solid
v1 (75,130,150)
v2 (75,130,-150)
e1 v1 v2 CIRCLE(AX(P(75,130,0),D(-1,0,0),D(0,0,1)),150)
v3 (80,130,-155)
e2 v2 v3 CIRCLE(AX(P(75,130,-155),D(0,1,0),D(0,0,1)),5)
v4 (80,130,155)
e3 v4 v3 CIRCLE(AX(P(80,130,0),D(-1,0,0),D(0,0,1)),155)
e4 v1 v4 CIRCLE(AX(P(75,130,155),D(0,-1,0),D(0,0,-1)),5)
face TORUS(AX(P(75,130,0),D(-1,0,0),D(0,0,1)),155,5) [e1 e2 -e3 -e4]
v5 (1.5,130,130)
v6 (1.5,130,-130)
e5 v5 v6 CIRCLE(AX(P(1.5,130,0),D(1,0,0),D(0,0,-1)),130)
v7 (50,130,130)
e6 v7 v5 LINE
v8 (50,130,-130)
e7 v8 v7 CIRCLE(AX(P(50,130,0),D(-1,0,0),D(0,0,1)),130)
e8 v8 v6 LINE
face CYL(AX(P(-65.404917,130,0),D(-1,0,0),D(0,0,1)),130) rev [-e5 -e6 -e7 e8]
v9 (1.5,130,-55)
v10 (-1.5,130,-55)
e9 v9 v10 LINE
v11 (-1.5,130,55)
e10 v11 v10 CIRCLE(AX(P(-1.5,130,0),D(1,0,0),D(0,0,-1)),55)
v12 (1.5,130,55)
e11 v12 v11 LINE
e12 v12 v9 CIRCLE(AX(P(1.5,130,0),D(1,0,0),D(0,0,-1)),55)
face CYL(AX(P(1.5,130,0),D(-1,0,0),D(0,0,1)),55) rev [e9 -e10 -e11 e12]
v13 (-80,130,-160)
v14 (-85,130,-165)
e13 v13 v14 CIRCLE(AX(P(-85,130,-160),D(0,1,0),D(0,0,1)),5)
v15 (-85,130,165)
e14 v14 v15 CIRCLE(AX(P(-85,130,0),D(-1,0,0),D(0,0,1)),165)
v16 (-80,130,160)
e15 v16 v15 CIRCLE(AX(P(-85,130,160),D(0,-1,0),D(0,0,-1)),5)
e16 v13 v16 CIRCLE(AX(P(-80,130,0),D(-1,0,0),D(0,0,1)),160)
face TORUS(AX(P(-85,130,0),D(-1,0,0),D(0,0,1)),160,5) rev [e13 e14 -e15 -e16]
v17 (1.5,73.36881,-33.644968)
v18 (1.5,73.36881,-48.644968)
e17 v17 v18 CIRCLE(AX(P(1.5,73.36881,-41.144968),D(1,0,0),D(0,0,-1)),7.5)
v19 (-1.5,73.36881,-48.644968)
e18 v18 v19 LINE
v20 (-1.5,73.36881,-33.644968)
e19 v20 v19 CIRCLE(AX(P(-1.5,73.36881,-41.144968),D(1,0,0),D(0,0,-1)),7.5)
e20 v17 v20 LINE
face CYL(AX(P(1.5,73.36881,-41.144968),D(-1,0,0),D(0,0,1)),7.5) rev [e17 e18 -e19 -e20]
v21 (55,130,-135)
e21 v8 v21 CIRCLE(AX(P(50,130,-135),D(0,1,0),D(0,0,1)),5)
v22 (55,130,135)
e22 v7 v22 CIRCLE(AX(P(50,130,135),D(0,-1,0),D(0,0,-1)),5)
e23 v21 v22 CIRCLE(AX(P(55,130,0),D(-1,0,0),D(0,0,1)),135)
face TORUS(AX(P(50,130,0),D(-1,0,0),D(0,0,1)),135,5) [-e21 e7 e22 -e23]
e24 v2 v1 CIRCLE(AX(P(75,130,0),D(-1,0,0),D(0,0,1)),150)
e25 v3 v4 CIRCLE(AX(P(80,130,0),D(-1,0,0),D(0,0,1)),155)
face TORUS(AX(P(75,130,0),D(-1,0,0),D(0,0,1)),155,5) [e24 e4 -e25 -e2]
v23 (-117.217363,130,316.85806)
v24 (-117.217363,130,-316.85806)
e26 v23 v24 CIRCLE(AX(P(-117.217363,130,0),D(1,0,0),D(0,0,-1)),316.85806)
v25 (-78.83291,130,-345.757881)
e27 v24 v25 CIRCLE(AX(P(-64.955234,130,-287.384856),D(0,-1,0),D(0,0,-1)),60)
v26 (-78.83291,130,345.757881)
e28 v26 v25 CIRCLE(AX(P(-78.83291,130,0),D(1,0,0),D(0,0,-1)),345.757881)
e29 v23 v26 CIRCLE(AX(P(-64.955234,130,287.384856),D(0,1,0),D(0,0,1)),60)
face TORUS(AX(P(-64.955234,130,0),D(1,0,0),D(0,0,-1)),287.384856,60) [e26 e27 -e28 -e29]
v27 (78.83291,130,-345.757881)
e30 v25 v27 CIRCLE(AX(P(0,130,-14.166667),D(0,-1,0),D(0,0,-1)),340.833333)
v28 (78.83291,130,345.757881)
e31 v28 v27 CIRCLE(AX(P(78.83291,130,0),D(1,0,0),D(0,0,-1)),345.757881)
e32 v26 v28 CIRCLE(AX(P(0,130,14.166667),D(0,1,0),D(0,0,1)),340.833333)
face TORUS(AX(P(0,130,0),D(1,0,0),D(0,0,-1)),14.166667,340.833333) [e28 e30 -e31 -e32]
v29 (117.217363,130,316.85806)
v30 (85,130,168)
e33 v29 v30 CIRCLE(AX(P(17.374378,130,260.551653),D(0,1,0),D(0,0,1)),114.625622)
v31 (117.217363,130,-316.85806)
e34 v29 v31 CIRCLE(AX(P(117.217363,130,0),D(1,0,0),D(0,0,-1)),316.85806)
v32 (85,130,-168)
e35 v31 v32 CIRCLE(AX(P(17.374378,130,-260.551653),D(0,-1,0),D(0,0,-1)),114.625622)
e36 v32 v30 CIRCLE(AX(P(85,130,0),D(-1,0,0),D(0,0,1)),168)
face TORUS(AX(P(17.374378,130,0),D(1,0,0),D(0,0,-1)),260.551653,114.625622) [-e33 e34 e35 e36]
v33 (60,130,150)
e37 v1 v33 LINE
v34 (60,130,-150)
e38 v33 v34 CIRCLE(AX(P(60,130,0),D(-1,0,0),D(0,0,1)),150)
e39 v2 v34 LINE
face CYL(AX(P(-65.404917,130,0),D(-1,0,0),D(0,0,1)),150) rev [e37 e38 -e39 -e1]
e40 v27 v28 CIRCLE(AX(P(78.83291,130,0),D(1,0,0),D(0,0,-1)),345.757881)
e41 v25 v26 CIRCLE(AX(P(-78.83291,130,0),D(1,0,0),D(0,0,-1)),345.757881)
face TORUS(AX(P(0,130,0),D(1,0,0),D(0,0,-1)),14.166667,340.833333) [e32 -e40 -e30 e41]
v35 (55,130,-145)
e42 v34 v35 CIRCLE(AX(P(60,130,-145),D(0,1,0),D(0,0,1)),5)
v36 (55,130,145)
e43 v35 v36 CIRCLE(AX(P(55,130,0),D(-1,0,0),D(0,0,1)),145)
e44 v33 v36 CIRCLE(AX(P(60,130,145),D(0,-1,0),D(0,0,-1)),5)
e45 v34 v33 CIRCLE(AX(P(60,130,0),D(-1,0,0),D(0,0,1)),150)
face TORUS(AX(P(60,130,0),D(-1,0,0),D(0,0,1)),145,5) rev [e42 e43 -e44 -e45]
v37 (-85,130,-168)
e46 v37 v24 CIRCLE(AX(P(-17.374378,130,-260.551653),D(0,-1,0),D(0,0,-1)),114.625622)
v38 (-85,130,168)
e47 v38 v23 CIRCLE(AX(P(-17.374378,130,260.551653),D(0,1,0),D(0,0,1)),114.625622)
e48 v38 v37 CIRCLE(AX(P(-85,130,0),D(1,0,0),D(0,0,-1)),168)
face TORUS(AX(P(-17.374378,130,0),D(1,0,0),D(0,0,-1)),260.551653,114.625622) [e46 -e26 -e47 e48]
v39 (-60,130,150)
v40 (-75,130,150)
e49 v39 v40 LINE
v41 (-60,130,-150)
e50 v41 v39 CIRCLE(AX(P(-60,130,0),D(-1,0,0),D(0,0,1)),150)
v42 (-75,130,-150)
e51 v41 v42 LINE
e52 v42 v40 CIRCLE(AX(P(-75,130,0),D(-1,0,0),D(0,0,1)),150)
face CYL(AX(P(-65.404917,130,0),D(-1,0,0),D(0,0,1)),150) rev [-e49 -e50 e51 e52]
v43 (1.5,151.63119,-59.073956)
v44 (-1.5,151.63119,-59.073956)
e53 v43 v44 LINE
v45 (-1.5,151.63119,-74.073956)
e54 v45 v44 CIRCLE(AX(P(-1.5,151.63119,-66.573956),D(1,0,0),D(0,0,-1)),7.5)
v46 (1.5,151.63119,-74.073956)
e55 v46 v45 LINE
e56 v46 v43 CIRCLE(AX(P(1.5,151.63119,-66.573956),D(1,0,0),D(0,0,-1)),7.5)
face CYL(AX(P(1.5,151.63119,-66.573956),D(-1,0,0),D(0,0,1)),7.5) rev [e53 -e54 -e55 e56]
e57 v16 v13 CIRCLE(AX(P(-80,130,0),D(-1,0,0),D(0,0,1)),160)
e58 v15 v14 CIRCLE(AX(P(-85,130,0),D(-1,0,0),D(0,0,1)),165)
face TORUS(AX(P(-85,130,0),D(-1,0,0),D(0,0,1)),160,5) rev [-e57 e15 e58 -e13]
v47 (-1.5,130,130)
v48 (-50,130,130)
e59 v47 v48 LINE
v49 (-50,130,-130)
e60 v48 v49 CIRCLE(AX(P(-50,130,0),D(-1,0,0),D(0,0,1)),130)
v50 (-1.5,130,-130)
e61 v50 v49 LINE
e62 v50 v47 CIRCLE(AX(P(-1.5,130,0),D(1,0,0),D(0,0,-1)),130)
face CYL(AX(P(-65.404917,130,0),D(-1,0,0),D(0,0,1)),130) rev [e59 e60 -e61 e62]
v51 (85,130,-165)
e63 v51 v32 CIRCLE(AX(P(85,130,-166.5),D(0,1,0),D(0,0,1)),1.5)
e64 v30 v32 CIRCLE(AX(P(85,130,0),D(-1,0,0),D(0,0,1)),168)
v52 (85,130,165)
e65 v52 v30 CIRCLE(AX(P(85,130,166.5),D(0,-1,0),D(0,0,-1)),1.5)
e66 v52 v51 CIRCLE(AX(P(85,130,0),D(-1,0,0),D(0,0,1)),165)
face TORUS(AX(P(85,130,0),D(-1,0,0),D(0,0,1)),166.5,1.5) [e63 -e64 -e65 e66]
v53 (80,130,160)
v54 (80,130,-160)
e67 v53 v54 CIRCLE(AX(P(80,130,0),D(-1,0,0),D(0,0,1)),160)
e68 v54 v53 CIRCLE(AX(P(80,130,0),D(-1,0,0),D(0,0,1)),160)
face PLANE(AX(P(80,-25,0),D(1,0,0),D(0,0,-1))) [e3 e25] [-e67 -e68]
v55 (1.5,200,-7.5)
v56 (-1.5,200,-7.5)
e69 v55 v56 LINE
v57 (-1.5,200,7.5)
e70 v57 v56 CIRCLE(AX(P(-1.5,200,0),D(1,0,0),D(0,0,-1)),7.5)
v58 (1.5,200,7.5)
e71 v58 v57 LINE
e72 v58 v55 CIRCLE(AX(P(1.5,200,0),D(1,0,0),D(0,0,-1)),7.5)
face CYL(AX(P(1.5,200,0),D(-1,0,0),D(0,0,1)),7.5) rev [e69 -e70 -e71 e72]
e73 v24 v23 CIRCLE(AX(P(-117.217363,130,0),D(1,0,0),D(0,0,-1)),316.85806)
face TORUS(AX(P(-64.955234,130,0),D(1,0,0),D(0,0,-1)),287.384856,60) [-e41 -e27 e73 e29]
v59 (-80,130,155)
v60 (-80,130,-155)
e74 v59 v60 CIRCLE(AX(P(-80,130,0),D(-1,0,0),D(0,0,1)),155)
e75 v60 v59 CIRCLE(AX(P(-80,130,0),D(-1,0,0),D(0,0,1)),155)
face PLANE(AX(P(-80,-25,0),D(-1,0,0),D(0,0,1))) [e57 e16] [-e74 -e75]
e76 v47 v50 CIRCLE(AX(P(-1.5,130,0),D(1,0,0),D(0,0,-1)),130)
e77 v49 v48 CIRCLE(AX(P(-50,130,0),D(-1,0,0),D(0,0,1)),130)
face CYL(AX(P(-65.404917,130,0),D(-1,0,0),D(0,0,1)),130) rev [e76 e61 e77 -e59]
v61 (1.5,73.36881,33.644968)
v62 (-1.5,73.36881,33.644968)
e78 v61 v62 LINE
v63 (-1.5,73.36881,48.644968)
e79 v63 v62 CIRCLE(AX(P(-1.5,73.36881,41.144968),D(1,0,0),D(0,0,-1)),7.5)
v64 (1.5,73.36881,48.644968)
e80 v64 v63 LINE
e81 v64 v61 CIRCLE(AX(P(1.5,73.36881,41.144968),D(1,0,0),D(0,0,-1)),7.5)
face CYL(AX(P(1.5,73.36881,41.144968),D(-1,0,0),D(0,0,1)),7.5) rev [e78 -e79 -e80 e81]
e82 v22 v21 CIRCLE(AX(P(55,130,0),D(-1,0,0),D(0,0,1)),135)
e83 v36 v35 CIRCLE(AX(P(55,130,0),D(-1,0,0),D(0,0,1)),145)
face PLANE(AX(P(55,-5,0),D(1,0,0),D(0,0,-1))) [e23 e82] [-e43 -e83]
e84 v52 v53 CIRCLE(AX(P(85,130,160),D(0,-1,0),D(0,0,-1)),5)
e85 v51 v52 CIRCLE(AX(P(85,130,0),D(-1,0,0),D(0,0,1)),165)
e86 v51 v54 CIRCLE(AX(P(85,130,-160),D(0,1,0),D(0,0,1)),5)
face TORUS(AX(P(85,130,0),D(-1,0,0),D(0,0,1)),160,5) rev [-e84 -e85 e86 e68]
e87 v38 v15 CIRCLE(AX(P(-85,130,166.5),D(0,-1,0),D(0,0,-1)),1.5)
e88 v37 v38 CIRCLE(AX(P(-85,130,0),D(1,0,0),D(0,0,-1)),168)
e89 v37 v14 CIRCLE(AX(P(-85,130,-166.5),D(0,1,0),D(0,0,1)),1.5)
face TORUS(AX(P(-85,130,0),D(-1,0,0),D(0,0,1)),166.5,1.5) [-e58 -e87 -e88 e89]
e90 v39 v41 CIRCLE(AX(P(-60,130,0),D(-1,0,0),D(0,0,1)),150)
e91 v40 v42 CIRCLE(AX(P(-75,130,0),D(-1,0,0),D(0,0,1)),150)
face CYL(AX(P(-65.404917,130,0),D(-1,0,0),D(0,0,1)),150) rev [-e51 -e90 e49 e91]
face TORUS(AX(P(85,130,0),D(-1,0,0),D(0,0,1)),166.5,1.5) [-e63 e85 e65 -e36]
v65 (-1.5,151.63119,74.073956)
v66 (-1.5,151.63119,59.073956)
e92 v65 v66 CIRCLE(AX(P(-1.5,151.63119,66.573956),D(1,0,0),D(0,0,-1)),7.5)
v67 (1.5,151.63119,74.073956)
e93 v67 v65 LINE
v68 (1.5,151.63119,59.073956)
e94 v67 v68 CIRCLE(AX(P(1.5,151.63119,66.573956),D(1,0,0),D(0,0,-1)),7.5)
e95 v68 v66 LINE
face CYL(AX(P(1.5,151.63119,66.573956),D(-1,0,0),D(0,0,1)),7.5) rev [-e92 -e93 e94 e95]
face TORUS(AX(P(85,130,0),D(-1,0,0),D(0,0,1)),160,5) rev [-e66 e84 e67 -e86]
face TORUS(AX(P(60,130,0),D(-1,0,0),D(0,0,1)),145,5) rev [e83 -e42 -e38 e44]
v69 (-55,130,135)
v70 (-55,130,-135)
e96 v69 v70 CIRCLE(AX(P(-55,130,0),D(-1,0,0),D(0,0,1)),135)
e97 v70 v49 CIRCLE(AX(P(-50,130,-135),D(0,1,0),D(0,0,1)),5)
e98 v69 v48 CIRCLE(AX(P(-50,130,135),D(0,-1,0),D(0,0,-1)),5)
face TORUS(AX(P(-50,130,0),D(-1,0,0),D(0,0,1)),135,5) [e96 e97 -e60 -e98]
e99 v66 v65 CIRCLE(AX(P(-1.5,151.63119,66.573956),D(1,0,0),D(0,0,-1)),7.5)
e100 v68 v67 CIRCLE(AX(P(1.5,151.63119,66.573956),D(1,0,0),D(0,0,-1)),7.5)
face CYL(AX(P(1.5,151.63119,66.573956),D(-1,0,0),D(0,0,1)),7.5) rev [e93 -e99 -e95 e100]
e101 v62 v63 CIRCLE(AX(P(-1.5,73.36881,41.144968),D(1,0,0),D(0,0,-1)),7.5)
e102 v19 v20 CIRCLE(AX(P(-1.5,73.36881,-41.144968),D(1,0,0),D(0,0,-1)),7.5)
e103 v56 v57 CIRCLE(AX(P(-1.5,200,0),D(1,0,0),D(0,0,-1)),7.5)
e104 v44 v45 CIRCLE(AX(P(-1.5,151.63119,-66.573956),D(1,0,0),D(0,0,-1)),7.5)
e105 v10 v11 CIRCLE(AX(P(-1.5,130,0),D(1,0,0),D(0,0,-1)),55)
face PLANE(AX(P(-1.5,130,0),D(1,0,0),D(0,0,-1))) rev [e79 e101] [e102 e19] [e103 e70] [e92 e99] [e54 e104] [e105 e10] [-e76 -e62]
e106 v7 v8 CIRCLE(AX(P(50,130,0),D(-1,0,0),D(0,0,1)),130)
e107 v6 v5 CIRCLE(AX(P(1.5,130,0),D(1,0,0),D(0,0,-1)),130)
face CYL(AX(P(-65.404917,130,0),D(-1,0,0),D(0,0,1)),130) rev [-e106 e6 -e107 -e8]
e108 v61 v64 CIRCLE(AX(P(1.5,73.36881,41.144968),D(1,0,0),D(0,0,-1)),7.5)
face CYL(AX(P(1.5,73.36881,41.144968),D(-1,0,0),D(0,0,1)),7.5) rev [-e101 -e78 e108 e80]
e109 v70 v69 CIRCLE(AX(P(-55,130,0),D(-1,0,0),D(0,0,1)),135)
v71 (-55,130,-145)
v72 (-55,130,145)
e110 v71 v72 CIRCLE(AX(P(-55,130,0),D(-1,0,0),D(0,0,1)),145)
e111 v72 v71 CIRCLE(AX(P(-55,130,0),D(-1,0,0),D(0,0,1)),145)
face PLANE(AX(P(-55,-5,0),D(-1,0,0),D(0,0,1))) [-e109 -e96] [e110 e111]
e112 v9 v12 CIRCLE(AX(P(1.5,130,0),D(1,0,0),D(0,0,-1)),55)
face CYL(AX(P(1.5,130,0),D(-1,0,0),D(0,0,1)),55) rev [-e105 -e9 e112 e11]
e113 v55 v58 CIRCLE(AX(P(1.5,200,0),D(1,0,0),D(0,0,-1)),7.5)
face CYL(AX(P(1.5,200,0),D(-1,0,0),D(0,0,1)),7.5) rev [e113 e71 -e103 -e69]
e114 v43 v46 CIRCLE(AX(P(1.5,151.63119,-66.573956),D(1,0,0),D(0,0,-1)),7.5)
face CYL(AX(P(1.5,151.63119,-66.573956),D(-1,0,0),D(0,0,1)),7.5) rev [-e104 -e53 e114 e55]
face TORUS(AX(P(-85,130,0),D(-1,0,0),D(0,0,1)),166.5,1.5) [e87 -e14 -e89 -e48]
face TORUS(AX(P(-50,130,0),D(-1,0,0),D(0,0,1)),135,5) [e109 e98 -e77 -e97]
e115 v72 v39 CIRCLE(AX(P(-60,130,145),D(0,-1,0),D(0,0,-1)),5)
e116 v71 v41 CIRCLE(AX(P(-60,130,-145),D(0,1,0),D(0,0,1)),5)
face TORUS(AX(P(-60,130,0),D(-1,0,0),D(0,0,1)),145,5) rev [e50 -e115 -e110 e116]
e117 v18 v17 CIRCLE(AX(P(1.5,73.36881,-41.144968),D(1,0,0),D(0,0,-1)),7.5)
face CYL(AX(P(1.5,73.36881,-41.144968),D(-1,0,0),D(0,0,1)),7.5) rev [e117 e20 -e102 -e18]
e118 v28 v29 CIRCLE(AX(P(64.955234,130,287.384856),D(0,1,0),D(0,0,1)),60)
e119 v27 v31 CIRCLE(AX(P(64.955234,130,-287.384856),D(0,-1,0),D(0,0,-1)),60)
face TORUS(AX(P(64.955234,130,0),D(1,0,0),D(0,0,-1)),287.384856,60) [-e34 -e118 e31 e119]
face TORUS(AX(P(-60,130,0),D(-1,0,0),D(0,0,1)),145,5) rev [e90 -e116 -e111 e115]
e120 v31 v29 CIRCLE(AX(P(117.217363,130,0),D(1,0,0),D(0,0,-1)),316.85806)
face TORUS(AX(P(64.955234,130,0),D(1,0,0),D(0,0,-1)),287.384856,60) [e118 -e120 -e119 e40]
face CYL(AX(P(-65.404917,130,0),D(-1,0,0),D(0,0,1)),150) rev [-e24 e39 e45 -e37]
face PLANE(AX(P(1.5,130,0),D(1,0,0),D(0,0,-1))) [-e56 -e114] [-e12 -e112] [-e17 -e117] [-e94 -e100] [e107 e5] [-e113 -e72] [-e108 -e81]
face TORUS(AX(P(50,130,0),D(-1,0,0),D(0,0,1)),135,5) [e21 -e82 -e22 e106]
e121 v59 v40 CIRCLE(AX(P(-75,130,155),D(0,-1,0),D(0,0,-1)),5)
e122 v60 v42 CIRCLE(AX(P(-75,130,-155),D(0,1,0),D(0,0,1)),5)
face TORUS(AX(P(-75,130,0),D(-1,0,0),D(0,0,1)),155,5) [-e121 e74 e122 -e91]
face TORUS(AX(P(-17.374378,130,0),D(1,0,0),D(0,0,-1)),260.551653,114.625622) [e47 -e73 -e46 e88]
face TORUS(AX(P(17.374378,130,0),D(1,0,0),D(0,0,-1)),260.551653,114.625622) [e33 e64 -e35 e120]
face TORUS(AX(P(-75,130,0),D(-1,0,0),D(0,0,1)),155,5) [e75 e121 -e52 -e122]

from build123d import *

# Parameters (mm, degrees)
SKETCH_2_R      = 130
SKETCH_2_R_2    = 55
SKETCH_2_R_3    = 7.5
EXTRUDE_1_DEPTH = 1.5


with BuildPart() as part:
    # 草图1 → 旋转1 (revolve)
    with BuildSketch(Plane.XY, mode=Mode.PRIVATE) as revolve_1_sk:
        with BuildLine():
            Line((-50, 0), (50, 0))
            ThreePointArc((50, 0), (53.535533906, -1.464466094), (55, -5))
            Line((55, -5), (55, -15))
            ThreePointArc((55, -15), (56.464466094, -18.535533906), (60, -20))
            Line((60, -20), (75, -20))
            ThreePointArc((75, -20), (78.535533906, -21.464466094), (80, -25))
            Line((80, -25), (80, -30))
            ThreePointArc((80, -30), (81.464466094, -33.535533906), (85, -35))
            ThreePointArc((85, -35), (86.5, -36.5), (85, -38))
            ThreePointArc((85, -38), (79.343145751, -35.656854249), (77, -30))
            Line((77, -30), (77, -25))
            ThreePointArc((77, -25), (76.414213562, -23.585786438), (75, -23))
            Line((75, -23), (60, -23))
            ThreePointArc((60, -23), (54.343145751, -20.656854249), (52, -15))
            Line((52, -15), (52, -5))
            ThreePointArc((52, -5), (51.414213562, -3.585786438), (50, -3))
            Line((50, -3), (-50, -3))
            ThreePointArc((-50, -3), (-51.414213562, -3.585786438), (-52, -5))
            Line((-52, -5), (-52, -15))
            ThreePointArc((-52, -15), (-54.343145751, -20.656854249), (-60, -23))
            Line((-60, -23), (-75, -23))
            ThreePointArc((-75, -23), (-76.414213562, -23.585786438), (-77, -25))
            Line((-77, -25), (-77, -30))
            ThreePointArc((-77, -30), (-79.343145751, -35.656854249), (-85, -38))
            ThreePointArc((-85, -38), (-86.5, -36.5), (-85, -35))
            ThreePointArc((-85, -35), (-81.464466094, -33.535533906), (-80, -30))
            Line((-80, -30), (-80, -25))
            ThreePointArc((-80, -25), (-78.535533906, -21.464466094), (-75, -20))
            Line((-75, -20), (-60, -20))
            ThreePointArc((-60, -20), (-56.464466094, -18.535533906), (-55, -15))
            Line((-55, -15), (-55, -5))
            ThreePointArc((-55, -5), (-53.535533906, -1.464466094), (-50, 0))
        make_face()
    revolve(revolve_1_sk.sketch.rotate(Axis((-65.404917461, 130, 0), (1, 0, 0)), 270), axis=Axis((-65.404917461, 130, 0), (1, 0, 0)))



with BuildPart() as body_2:
    # 草图2 → 凸台-拉伸1 (new, symmetric)
    with BuildSketch(Plane(origin=(0, 0, 0), x_dir=(0, 0, -1), z_dir=(1, 0, 0))):
        with Locations(Location((0, 130, 0), (0, 0, 180))):
            Circle(SKETCH_2_R)
        with Locations((0, 130)):
            Circle(SKETCH_2_R_2, mode=Mode.SUBTRACT)
        with Locations((0, 200)):
            Circle(SKETCH_2_R_3, mode=Mode.SUBTRACT)
        with Locations((66.573956141, 151.631189606)):
            Circle(SKETCH_2_R_3, mode=Mode.SUBTRACT)
        with Locations((41.14496766, 73.368810394)):
            Circle(SKETCH_2_R_3, mode=Mode.SUBTRACT)
        with Locations((-41.14496766, 73.368810394)):
            Circle(SKETCH_2_R_3, mode=Mode.SUBTRACT)
        with Locations((-66.573956141, 151.631189606)):
            Circle(SKETCH_2_R_3, mode=Mode.SUBTRACT)
    extrude(amount=EXTRUDE_1_DEPTH, both=True)


with BuildPart() as part_1:
    add(part.part)

    add(body_2.part)  # 旋转2 merges body 2
    # 草图3 → 旋转2 (revolve)
    with BuildSketch(Plane.XY, mode=Mode.PRIVATE) as revolve_2_sk:
        with BuildLine():
            Line((-77, 285), (-77, 290))
            ThreePointArc((-77, 290), (-79.343145751, 295.656854249), (-85, 298))
            ThreePointArc((-85, 298), (-129.406133001, 366.30461016), (-117.217363461, 446.858060205))
            ThreePointArc((-117.217363461, 446.858060205), (-101.044267901, 465.317950684), (-78.832909756, 475.757881041))
            ThreePointArc((-78.832909756, 475.757881041), (0, 485), (78.832909756, 475.757881041))
            ThreePointArc((78.832909756, 475.757881041), (101.044267901, 465.317950684), (117.217363461, 446.858060205))
            ThreePointArc((117.217363461, 446.858060205), (129.406133001, 366.30461016), (85, 298))
            ThreePointArc((85, 298), (79.343145751, 295.656854249), (77, 290))
            Line((77, 290), (77, 285))
            ThreePointArc((77, 285), (76.414213562, 283.585786438), (75, 283))
            Line((75, 283), (60, 283))
            ThreePointArc((60, 283), (54.343145751, 280.656854249), (52, 275))
            Line((52, 275), (52, 265))
            ThreePointArc((52, 265), (51.414213562, 263.585786438), (50, 263))
            Line((50, 263), (-50, 263))
            ThreePointArc((-50, 263), (-51.414213562, 263.585786438), (-52, 265))
            Line((-52, 265), (-52, 275))
            ThreePointArc((-52, 275), (-54.343145751, 280.656854249), (-60, 283))
            Line((-60, 283), (-75, 283))
            ThreePointArc((-75, 283), (-76.414213562, 283.585786438), (-77, 285))
        make_face()
    revolve(revolve_2_sk.sketch.rotate(Axis((50, 130, 0), (-1, 0, 0)), 90), axis=Axis((50, 130, 0), (-1, 0, 0)))


solid = part_1.part
